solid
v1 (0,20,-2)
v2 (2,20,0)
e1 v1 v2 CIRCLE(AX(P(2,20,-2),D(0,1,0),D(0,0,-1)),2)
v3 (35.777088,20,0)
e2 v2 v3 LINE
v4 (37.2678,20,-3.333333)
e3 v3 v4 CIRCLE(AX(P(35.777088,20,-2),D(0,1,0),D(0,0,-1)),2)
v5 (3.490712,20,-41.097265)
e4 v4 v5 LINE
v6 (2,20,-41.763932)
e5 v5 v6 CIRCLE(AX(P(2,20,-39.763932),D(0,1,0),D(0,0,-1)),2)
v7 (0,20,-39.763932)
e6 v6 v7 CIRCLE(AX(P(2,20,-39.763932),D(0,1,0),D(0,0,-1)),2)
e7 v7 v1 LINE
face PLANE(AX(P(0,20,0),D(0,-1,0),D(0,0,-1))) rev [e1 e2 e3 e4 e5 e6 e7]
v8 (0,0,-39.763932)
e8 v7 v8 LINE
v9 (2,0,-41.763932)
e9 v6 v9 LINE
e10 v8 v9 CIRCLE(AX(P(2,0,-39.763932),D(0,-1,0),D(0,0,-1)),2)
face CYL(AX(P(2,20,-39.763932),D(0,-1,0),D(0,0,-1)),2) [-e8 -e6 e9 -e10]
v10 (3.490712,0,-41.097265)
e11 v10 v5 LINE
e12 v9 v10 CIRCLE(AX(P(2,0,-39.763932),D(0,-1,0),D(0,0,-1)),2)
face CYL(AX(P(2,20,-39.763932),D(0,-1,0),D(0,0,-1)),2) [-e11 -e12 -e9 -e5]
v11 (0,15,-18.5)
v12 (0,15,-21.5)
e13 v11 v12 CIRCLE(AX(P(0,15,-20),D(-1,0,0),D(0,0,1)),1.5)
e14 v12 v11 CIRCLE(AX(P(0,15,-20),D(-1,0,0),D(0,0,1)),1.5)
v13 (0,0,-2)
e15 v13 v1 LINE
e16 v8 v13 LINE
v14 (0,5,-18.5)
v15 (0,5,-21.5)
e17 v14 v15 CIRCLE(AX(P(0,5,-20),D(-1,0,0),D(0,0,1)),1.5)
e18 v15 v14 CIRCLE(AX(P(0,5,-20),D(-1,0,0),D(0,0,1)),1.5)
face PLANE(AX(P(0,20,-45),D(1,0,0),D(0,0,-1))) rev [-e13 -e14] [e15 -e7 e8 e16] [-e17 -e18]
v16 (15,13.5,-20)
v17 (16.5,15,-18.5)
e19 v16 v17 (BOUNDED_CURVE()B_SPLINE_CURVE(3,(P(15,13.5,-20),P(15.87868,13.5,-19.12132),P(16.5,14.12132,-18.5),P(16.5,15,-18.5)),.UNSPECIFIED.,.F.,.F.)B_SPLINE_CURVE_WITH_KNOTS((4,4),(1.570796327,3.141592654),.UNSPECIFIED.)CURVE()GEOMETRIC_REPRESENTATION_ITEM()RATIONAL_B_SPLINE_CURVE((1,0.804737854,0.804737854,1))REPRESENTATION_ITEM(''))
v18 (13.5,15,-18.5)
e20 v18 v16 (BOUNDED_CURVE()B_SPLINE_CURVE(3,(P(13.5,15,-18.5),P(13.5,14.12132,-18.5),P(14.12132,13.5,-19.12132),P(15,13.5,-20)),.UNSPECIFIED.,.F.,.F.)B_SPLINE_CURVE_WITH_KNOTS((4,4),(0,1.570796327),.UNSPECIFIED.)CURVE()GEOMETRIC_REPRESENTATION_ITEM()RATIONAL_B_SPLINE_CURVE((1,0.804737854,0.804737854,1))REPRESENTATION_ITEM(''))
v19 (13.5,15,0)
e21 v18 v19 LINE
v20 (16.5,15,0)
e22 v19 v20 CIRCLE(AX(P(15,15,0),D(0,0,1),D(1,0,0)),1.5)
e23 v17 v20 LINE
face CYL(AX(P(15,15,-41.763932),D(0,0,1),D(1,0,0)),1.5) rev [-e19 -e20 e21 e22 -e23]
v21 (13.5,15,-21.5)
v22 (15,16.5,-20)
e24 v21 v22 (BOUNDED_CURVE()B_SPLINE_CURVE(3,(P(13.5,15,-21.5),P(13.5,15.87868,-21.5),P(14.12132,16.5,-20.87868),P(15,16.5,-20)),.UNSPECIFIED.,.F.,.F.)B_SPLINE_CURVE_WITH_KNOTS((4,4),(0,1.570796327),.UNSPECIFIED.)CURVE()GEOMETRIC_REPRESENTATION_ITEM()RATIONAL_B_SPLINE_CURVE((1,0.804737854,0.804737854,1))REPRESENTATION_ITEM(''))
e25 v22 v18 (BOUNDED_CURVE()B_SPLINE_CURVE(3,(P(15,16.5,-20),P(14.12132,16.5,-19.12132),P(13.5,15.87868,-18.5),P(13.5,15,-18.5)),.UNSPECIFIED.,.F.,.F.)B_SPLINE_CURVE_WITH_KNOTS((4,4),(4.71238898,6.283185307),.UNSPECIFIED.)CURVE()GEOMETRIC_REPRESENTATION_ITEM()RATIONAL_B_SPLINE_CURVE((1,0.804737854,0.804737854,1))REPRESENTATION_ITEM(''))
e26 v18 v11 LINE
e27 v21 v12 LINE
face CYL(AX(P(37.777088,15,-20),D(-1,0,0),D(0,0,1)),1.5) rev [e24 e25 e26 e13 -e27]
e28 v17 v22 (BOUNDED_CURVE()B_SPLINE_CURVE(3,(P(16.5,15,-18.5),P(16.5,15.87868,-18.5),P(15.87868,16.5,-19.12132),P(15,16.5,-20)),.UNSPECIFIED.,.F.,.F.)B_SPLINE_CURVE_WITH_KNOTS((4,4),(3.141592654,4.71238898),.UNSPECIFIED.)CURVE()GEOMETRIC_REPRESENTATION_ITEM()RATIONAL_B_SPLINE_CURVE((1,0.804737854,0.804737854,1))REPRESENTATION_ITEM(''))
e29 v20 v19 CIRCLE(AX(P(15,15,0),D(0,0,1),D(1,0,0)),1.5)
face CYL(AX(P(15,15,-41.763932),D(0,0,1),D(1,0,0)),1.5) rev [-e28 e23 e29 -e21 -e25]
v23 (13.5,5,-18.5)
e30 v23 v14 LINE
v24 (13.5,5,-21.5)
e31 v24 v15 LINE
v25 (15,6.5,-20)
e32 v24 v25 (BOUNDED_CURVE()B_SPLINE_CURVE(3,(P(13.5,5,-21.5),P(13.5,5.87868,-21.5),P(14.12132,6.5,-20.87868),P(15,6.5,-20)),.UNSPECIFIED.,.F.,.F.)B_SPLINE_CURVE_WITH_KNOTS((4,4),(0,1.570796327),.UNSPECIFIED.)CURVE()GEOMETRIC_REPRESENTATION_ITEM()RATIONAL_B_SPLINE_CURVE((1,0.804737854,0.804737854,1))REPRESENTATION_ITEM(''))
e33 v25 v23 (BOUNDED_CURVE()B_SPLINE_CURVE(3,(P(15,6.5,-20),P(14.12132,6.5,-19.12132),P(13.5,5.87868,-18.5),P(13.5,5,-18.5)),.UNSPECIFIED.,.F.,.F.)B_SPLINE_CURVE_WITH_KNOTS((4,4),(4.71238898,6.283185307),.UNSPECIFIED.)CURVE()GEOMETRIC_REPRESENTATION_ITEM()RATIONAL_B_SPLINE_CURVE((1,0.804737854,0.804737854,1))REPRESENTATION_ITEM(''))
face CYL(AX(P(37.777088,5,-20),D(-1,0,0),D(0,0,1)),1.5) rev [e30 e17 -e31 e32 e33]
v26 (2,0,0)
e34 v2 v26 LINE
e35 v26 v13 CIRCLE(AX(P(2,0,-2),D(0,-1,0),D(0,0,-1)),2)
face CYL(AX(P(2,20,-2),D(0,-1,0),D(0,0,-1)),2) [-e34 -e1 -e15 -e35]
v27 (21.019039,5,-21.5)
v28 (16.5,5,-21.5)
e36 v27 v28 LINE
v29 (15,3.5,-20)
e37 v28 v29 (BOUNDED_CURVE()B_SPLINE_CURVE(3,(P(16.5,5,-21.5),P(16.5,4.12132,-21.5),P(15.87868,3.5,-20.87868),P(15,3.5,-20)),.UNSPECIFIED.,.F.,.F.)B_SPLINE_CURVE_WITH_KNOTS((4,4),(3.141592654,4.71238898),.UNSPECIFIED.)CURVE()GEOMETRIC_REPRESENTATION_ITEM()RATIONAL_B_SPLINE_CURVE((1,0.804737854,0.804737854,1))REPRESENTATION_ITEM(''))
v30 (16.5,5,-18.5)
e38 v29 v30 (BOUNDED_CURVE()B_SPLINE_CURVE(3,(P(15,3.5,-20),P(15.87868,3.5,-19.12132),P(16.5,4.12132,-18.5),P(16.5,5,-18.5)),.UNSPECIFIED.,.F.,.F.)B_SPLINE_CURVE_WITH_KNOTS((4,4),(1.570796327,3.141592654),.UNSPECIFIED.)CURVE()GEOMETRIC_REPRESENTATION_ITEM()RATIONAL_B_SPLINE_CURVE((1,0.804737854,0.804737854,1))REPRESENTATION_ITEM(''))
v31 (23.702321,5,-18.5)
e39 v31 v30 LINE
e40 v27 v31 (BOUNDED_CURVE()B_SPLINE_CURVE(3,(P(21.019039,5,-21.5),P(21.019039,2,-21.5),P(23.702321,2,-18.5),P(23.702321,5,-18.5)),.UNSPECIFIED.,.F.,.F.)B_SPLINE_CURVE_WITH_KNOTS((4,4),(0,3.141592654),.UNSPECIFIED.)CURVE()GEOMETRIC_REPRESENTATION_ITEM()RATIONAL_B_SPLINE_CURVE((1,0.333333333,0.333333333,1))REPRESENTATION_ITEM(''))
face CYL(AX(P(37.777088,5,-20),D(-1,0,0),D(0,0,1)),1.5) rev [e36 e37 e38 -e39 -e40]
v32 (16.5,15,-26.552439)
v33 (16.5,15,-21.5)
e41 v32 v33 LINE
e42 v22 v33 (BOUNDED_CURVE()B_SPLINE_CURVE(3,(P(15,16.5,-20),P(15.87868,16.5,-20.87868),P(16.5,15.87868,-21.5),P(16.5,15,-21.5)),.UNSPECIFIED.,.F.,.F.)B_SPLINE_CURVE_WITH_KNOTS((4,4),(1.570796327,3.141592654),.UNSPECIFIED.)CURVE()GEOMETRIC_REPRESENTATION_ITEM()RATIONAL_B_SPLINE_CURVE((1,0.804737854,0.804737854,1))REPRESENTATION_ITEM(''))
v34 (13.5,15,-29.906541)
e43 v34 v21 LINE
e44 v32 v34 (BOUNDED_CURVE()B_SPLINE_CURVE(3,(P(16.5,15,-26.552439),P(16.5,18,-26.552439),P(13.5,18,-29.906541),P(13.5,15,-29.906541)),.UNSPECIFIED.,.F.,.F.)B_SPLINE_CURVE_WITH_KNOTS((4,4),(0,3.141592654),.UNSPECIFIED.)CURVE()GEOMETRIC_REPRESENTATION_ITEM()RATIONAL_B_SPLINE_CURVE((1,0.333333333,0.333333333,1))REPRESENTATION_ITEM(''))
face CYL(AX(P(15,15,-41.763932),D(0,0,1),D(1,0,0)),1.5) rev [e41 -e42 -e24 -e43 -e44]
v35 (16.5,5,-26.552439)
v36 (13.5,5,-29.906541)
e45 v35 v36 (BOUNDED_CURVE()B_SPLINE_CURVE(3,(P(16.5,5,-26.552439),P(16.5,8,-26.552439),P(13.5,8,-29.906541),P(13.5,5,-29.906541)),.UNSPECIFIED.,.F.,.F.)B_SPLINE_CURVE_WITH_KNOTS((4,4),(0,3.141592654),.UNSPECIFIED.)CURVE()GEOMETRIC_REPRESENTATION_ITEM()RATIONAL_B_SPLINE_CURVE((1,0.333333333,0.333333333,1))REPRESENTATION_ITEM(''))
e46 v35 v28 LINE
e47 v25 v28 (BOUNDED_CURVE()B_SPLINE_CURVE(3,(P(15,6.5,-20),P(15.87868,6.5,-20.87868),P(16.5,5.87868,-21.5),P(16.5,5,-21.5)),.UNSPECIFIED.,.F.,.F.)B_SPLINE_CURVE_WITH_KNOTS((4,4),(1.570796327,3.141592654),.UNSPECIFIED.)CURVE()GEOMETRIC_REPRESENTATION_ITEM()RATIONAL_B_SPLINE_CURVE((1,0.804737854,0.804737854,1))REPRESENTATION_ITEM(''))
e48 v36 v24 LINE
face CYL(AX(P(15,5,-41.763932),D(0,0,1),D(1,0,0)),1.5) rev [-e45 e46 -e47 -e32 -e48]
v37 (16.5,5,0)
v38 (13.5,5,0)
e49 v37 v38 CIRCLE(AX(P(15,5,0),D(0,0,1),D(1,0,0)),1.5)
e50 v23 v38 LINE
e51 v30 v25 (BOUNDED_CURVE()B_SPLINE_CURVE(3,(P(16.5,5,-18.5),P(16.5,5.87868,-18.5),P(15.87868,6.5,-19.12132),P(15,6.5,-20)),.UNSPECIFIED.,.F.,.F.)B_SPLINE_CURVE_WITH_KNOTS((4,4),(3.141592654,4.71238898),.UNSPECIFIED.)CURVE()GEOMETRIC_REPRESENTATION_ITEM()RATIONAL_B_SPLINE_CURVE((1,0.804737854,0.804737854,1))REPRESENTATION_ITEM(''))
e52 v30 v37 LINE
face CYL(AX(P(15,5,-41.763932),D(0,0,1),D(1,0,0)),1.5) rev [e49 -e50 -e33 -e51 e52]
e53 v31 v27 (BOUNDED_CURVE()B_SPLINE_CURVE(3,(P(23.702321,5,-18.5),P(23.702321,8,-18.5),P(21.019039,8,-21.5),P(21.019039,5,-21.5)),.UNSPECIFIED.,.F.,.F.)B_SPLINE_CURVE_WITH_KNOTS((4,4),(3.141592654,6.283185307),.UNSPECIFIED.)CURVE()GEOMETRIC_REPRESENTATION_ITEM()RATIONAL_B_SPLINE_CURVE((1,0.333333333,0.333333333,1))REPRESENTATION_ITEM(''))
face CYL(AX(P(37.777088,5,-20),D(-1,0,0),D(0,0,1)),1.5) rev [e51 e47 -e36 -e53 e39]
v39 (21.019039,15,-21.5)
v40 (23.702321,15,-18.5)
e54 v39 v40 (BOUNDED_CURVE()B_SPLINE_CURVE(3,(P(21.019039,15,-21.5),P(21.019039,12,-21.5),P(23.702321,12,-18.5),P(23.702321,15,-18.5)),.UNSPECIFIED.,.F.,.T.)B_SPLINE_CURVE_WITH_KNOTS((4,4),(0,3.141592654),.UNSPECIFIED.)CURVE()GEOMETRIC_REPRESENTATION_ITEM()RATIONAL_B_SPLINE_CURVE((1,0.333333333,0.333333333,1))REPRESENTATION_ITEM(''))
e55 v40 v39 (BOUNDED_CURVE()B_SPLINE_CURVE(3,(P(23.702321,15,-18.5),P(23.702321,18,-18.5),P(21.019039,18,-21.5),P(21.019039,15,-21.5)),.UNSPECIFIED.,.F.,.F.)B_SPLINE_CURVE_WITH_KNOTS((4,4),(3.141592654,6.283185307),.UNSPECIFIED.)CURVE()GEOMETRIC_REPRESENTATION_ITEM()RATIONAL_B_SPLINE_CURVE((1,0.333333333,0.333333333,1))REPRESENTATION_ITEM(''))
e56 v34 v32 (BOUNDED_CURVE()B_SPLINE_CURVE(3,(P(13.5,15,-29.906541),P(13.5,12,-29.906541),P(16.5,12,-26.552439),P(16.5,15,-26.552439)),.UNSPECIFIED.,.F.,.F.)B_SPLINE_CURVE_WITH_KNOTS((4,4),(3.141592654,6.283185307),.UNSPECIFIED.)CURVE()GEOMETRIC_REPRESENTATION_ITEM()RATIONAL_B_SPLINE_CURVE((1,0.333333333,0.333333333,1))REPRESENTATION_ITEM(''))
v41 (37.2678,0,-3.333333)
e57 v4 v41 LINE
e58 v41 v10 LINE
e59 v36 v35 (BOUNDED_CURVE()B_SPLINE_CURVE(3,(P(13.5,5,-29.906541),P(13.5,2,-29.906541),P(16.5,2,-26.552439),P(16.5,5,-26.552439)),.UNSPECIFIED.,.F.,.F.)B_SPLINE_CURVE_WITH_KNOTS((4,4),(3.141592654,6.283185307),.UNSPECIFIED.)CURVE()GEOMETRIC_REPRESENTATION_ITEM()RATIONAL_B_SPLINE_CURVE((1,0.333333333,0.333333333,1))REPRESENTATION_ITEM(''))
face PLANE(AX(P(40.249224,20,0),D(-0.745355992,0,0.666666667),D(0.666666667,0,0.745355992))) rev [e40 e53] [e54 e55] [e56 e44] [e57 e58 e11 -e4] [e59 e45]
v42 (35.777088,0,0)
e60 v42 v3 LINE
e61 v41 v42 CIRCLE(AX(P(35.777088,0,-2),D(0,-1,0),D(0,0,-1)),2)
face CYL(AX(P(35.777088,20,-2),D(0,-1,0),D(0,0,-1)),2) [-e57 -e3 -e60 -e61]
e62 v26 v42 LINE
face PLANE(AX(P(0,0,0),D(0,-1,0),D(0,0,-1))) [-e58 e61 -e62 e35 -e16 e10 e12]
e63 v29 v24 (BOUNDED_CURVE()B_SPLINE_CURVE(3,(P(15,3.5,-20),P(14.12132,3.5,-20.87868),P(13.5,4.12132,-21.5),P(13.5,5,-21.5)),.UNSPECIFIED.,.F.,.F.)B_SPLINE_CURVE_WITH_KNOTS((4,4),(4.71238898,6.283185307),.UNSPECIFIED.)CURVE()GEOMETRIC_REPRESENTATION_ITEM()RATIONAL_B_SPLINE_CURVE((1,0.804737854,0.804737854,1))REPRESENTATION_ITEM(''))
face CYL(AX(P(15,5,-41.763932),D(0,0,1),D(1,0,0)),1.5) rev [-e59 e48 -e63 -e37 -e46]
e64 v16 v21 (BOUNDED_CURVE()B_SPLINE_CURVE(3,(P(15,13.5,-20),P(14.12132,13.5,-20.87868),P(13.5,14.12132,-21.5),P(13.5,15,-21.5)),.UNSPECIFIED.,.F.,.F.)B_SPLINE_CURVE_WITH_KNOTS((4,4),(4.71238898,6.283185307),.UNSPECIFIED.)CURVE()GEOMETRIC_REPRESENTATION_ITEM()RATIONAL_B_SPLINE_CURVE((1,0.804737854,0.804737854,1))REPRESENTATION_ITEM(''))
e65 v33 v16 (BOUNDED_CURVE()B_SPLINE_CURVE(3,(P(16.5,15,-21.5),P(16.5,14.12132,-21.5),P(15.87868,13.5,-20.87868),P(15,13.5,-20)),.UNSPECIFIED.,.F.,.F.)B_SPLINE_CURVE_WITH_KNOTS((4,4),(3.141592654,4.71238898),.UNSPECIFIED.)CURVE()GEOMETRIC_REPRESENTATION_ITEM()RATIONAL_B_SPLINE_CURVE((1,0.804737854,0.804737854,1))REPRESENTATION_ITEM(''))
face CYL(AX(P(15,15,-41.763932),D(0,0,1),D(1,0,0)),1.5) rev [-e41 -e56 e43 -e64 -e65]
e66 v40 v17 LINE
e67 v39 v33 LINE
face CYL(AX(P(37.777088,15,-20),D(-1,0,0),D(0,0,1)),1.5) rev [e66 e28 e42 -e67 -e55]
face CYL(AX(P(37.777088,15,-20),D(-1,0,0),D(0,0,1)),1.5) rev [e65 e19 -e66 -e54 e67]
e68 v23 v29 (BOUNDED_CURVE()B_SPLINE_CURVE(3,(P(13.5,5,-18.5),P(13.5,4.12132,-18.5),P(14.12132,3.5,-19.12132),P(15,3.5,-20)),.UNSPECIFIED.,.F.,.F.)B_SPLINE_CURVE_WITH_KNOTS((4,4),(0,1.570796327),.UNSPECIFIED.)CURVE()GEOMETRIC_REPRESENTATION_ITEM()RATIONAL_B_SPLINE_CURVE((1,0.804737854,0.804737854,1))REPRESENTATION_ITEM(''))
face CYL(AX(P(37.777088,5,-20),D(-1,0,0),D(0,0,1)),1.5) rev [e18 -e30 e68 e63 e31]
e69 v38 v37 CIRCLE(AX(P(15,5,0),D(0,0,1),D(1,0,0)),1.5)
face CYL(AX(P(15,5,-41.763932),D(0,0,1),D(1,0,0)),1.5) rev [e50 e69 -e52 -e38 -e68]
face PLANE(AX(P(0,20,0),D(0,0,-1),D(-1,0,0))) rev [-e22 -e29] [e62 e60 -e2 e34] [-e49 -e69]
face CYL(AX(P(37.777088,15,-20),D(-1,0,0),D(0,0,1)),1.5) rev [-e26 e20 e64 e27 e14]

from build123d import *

# Parameters (mm, degrees)
EXTRUDE_1_DEPTH     = 20
FILLET_1_R          = 2
SKETCH_2_R          = 1.5
CUT_EXTRUDE_1_DEPTH = 60.760642304
SKETCH_3_R          = 1.5
CUT_EXTRUDE_2_DEPTH = 60.760642304


with BuildPart() as part:
    # 草图1 → 凸台-拉伸1 (new body)
    with BuildSketch(Plane(origin=(0, 0, 0), x_dir=(1, 0, 0), z_dir=(0, 1, 0))):
        Polygon((0, 45), (0, 0), (40.249223595, 0), align=None)
    extrude(amount=EXTRUDE_1_DEPTH)

    # 圆角1
    fillet_1_edges = [part.edges().sort_by_distance(p)[0] for p in [
        (40.249223595, 10, 0),
        (0, 10, 0),
        (0, 10, -45),
    ]]
    fillet(fillet_1_edges, radius=FILLET_1_R)

    # 草图2 → 切除-拉伸1 (cut, through all)
    with BuildSketch(Plane.ZY):
        with Locations((-20, 15)):
            Circle(SKETCH_2_R)
        with Locations((-20, 5)):
            Circle(SKETCH_2_R)
    extrude(amount=-CUT_EXTRUDE_1_DEPTH, mode=Mode.SUBTRACT)

    # 草图3 → 切除-拉伸2 (cut, through all)
    with BuildSketch(Plane.XY):
        with Locations((15, 15)):
            Circle(SKETCH_3_R)
        with Locations((15, 5)):
            Circle(SKETCH_3_R)
    extrude(amount=-CUT_EXTRUDE_2_DEPTH, mode=Mode.SUBTRACT)


solid = part.part
